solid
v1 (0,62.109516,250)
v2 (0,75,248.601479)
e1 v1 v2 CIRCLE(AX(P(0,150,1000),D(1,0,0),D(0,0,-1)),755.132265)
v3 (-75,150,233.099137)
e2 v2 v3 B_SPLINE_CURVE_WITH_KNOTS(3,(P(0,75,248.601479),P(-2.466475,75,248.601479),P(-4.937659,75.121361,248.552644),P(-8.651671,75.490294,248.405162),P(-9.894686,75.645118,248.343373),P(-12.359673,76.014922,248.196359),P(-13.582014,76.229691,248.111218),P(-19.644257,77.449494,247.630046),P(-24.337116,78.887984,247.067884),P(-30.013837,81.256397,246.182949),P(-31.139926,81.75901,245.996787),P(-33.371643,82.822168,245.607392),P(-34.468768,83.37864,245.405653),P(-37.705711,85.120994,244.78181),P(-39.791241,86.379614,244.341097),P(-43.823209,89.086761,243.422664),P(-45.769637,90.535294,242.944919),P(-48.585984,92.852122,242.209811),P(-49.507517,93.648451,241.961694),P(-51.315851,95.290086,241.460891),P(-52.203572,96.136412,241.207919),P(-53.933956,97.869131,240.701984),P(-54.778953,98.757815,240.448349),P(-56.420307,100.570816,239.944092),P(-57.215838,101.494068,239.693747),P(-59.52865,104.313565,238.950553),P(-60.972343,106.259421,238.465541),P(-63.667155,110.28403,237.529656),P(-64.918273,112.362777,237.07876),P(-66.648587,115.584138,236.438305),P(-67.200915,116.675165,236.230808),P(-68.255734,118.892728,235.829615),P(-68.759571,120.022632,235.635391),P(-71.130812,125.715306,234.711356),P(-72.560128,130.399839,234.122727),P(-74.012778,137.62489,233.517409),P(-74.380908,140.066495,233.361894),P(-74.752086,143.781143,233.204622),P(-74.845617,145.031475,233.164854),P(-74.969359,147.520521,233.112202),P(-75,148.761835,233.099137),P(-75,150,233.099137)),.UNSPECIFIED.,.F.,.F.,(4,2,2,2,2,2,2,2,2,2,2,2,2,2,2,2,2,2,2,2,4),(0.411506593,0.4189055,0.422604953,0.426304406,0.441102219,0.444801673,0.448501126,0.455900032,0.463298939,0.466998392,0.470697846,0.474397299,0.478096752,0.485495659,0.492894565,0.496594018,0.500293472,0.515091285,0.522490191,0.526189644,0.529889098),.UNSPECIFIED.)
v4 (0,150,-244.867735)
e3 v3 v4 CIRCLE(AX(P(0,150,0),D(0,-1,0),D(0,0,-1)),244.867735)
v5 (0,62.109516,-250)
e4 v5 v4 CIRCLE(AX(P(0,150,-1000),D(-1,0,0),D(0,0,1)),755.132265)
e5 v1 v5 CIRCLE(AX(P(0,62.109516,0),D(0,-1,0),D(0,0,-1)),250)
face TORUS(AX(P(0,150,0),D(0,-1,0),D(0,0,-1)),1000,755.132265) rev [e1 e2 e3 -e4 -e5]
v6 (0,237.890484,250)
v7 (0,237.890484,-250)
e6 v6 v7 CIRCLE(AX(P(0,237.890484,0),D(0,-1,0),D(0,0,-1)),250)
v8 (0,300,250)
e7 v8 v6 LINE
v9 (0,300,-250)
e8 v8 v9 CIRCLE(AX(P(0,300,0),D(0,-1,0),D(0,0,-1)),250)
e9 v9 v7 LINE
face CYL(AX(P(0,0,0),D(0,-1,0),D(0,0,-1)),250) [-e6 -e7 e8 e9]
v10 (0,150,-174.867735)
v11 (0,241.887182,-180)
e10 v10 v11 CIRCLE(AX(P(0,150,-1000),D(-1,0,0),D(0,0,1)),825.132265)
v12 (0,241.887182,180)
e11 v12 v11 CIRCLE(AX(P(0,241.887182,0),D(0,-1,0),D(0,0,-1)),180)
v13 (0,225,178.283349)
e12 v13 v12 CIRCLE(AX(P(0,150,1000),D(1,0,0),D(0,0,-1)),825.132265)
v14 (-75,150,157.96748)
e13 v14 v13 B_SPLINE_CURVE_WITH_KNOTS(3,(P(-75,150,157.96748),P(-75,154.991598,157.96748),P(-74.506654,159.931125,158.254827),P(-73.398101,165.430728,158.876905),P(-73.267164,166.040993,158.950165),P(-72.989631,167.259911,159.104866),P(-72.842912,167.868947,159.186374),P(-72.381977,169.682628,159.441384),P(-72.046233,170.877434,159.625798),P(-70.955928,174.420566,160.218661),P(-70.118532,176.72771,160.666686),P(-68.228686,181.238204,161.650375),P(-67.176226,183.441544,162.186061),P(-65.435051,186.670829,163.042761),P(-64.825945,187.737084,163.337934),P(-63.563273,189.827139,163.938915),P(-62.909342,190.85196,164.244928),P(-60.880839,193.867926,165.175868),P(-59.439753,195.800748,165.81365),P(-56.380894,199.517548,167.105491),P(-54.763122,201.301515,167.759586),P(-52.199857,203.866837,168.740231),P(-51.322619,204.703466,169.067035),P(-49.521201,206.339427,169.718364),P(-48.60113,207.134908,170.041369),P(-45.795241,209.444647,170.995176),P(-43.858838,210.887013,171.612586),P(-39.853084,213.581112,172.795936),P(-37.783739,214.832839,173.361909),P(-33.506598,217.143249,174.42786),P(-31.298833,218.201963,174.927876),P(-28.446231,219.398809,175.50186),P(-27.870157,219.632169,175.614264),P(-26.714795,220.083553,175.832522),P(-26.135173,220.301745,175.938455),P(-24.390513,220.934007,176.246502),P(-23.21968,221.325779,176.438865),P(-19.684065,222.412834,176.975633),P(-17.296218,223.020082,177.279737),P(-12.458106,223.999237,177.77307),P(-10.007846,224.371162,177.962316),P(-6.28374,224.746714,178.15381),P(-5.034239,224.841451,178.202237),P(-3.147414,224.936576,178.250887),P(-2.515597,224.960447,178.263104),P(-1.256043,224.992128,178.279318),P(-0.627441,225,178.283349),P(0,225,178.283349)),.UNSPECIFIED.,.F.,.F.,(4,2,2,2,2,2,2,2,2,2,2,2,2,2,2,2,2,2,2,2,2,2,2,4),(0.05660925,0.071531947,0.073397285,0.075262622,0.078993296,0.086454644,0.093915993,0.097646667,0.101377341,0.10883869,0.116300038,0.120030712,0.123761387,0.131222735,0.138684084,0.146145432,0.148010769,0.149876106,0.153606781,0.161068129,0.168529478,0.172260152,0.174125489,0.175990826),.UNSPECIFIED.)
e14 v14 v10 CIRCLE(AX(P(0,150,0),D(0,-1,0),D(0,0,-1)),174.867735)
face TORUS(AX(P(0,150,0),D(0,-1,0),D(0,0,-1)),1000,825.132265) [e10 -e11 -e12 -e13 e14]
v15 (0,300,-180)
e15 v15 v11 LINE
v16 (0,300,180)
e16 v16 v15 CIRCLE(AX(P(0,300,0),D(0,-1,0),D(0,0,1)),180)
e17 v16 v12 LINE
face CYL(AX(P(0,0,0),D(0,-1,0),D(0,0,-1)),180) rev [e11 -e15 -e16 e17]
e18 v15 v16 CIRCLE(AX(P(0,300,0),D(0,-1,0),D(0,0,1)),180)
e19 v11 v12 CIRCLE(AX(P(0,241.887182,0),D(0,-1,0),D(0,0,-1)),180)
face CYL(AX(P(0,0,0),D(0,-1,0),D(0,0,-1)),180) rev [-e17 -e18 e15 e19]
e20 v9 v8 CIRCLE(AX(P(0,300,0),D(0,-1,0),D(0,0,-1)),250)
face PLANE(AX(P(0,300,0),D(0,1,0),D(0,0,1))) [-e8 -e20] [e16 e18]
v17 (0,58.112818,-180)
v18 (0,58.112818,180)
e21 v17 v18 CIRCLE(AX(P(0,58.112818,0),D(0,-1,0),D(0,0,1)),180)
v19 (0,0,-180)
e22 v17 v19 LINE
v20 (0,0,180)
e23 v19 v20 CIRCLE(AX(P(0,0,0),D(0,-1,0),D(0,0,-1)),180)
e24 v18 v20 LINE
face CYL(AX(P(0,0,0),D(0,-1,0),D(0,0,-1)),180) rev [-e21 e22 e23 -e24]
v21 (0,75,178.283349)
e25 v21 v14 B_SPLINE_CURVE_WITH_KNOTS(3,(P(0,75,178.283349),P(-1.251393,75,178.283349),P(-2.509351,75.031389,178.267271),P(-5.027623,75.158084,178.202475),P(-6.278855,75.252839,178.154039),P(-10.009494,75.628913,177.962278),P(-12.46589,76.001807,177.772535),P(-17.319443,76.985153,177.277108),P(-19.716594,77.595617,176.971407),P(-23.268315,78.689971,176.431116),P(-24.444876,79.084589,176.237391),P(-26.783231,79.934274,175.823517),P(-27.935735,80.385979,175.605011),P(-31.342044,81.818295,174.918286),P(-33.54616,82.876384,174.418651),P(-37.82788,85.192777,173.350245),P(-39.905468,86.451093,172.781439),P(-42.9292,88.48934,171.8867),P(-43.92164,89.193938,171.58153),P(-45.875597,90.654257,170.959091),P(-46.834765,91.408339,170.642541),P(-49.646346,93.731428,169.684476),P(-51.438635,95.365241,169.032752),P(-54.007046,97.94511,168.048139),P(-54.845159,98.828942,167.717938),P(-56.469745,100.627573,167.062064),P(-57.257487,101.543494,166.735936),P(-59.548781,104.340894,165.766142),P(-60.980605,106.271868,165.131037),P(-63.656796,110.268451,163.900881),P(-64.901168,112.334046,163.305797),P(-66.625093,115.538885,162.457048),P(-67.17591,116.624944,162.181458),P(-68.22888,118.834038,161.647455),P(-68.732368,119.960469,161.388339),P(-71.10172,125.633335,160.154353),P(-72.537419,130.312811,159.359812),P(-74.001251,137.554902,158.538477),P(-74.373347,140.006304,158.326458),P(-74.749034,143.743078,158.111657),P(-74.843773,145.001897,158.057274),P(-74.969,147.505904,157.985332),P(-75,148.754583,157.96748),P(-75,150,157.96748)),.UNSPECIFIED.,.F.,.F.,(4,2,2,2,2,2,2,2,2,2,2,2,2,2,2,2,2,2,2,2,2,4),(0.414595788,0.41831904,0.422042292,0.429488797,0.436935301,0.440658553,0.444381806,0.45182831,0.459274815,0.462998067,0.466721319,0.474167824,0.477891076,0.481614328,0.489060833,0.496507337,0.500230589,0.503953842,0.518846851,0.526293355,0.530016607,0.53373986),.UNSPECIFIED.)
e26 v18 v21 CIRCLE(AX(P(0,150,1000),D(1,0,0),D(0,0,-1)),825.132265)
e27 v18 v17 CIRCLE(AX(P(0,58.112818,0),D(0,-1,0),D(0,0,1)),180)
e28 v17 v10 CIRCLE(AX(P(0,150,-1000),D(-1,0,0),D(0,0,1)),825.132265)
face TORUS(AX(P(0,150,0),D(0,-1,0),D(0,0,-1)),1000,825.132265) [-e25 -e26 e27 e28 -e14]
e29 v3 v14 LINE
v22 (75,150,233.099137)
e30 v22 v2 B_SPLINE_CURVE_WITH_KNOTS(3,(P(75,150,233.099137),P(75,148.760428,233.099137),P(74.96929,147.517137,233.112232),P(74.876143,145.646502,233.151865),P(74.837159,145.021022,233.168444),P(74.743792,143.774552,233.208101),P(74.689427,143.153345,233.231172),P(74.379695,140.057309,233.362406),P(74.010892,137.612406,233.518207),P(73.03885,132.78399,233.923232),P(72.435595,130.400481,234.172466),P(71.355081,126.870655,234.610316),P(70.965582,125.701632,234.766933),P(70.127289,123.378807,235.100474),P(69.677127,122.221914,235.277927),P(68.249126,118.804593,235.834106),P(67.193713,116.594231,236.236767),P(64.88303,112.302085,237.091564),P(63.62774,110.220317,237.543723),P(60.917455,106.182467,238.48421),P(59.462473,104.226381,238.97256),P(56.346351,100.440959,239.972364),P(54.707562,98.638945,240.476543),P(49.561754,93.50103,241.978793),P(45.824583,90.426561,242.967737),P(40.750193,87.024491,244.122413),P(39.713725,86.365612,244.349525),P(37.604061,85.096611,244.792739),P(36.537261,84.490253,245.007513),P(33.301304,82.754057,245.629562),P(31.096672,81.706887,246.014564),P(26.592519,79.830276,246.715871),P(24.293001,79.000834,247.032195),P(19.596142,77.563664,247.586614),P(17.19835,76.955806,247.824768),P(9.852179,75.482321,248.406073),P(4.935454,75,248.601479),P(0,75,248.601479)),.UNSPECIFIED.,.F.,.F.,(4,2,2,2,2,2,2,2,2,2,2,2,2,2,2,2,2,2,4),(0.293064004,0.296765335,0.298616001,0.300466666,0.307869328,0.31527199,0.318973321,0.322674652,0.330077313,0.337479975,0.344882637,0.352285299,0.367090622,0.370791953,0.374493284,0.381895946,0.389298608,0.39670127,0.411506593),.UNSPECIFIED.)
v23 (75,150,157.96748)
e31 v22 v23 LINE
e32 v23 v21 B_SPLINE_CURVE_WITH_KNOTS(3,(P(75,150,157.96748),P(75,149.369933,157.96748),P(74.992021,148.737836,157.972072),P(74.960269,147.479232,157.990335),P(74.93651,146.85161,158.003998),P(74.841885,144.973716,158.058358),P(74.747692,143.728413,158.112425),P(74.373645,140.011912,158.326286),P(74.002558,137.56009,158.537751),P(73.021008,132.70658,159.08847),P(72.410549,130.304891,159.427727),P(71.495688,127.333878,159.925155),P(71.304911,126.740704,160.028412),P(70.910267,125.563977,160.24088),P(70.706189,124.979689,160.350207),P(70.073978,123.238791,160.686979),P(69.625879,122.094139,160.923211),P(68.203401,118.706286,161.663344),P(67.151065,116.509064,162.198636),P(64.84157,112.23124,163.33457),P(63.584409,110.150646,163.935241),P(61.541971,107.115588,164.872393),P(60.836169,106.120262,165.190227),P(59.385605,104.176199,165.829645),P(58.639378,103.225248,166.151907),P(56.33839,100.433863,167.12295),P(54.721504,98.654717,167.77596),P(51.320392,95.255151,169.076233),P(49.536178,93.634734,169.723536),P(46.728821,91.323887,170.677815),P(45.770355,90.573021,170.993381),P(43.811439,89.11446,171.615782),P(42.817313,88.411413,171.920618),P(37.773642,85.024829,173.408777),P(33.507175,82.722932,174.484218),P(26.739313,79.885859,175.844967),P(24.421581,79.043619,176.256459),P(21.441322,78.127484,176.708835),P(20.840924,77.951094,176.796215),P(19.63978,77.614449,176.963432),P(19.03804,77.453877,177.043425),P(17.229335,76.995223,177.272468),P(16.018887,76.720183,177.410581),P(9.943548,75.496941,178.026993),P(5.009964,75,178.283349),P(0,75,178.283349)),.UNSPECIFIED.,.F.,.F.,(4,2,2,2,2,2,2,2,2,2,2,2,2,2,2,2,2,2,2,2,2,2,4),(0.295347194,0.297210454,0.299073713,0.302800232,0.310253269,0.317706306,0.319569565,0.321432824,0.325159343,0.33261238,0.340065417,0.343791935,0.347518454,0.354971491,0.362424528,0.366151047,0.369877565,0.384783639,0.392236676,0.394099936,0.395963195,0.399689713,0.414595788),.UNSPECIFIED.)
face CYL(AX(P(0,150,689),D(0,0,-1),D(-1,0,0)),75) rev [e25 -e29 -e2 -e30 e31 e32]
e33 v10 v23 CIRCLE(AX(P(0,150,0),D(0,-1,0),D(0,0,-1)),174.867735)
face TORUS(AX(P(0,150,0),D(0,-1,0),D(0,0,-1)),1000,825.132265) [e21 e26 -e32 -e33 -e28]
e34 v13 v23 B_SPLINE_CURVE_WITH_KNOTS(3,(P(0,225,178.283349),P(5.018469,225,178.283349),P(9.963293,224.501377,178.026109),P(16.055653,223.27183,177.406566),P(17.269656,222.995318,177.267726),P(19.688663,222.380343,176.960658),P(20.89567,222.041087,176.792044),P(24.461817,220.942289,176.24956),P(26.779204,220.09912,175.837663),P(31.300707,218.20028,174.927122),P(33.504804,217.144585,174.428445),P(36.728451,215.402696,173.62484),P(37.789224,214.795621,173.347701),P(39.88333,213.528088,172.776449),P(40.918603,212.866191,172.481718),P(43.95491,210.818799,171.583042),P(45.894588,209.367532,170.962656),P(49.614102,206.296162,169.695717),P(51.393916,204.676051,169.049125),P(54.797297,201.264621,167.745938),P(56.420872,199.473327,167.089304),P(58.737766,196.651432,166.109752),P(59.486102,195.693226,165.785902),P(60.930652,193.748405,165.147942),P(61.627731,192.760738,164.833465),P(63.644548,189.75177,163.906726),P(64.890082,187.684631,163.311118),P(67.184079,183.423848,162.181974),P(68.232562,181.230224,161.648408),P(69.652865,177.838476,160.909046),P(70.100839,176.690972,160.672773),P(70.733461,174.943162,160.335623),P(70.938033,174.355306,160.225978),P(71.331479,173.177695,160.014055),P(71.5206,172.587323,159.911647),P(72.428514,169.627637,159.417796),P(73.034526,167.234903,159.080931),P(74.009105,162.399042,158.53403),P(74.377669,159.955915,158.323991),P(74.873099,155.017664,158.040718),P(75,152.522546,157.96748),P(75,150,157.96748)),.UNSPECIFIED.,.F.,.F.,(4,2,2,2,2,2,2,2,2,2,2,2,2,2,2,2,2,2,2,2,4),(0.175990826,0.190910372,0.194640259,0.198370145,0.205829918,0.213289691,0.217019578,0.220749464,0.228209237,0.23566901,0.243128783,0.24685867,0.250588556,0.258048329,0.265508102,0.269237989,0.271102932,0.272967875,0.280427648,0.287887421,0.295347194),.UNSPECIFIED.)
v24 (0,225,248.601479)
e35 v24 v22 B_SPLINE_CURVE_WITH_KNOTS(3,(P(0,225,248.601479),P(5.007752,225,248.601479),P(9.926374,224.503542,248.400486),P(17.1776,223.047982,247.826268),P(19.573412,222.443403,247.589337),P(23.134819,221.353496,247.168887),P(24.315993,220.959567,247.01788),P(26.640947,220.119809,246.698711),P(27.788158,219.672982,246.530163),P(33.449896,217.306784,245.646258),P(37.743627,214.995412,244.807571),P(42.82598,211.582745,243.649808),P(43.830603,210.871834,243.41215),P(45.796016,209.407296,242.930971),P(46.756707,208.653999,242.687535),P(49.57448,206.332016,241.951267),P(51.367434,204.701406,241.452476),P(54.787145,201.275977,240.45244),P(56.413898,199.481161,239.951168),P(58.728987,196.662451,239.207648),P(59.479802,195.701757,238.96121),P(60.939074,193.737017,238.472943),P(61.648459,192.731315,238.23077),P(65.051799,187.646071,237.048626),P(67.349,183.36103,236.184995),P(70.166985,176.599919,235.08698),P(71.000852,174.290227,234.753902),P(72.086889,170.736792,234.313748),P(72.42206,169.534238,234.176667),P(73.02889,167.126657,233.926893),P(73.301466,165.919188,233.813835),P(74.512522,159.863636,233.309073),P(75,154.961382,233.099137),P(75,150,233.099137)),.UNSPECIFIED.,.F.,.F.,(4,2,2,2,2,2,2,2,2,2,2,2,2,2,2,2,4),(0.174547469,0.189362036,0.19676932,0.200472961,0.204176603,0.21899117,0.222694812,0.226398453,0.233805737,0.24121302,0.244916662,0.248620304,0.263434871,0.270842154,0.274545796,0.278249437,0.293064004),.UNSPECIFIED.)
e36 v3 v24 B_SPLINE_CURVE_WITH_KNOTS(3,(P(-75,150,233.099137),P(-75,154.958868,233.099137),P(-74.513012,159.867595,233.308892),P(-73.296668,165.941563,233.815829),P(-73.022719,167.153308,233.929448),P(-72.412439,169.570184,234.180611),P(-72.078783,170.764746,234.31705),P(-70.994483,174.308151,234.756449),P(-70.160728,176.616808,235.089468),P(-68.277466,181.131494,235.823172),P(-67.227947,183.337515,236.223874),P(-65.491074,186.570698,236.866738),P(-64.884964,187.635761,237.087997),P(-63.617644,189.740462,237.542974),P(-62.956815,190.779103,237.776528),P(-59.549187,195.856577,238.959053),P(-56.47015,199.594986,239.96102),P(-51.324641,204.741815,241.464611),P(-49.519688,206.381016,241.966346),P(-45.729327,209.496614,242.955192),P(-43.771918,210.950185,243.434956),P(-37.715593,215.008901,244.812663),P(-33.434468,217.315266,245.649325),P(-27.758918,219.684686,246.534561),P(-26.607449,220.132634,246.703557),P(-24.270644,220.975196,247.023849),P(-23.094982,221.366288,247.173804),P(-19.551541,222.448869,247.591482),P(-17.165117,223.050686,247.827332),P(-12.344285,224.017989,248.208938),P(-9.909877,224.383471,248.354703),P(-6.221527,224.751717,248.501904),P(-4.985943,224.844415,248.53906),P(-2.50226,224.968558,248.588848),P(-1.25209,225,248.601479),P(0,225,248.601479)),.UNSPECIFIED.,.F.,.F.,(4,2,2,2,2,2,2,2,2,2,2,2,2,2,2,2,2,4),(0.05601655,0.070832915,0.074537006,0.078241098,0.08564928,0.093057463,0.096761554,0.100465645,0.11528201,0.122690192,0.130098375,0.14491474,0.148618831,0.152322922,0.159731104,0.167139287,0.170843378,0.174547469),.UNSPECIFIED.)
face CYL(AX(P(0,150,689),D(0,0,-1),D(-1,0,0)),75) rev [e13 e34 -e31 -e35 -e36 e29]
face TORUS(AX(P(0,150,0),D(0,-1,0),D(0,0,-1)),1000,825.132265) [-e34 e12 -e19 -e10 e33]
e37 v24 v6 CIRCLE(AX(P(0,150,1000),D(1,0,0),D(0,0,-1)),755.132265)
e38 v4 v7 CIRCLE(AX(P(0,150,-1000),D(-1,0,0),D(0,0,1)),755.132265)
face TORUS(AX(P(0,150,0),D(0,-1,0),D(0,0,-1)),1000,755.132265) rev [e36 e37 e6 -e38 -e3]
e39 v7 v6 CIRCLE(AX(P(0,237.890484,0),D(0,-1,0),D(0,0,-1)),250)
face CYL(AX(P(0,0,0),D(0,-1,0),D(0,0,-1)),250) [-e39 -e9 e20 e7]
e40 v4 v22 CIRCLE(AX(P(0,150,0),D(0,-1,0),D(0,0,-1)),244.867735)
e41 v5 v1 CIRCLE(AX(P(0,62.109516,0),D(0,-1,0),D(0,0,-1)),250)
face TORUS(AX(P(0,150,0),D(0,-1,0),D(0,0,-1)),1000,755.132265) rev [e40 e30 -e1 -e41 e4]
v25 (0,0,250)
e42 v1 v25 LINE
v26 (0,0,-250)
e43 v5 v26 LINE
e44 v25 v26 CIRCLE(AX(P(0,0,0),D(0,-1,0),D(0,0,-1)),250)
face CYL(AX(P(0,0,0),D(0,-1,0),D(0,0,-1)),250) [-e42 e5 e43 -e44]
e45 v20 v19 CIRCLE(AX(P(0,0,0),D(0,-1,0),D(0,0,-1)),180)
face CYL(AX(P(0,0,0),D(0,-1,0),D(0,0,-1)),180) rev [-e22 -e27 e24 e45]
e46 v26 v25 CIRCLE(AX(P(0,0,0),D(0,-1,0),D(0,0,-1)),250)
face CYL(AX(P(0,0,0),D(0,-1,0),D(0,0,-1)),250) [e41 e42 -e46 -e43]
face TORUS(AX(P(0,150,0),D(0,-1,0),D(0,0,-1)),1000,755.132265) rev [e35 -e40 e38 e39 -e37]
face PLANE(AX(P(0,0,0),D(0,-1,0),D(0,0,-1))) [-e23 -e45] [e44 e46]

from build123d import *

# Parameters (mm, degrees)
SHELL1_T           = -70
SKETCH2_R          = 75
CUT_EXTRUDE1_DEPTH = 689


with BuildPart() as part:
    # Sketch1 → Revolve1 (revolve)
    with BuildSketch(Plane.XY, mode=Mode.PRIVATE) as revolve1_sk:
        with BuildLine():
            Line((0, 0), (0, 300))
            Line((0, 300), (250, 300))
            Line((250, 300), (250, 237.890484124))
            ThreePointArc((250, 237.890484124), (244.867735294, 150), (250, 62.109515876))
            Line((250, 62.109515876), (250, 0))
            Line((250, 0), (0, 0))
        make_face()
    revolve(revolve1_sk.sketch.rotate(Axis((0, 0, 0), (0, 1, 0)), 90), axis=Axis((0, 0, 0), (0, 1, 0)))

    # Shell1
    shell1_openings = [part.faces().sort_by_distance(p)[0] for p in [
        (0, 300, 0),
        (0, 0, 0),
    ]]
    offset(amount=SHELL1_T, openings=shell1_openings, kind=Kind.INTERSECTION)

    # Sketch2 → Cut-Extrude1 (cut)
    with BuildSketch(Plane.XY):
        with Locations(Location((0, 150, 0), (0, 0, 222.553028983))):
            Circle(SKETCH2_R)
    extrude(amount=CUT_EXTRUDE1_DEPTH, mode=Mode.SUBTRACT)


solid = part.part
